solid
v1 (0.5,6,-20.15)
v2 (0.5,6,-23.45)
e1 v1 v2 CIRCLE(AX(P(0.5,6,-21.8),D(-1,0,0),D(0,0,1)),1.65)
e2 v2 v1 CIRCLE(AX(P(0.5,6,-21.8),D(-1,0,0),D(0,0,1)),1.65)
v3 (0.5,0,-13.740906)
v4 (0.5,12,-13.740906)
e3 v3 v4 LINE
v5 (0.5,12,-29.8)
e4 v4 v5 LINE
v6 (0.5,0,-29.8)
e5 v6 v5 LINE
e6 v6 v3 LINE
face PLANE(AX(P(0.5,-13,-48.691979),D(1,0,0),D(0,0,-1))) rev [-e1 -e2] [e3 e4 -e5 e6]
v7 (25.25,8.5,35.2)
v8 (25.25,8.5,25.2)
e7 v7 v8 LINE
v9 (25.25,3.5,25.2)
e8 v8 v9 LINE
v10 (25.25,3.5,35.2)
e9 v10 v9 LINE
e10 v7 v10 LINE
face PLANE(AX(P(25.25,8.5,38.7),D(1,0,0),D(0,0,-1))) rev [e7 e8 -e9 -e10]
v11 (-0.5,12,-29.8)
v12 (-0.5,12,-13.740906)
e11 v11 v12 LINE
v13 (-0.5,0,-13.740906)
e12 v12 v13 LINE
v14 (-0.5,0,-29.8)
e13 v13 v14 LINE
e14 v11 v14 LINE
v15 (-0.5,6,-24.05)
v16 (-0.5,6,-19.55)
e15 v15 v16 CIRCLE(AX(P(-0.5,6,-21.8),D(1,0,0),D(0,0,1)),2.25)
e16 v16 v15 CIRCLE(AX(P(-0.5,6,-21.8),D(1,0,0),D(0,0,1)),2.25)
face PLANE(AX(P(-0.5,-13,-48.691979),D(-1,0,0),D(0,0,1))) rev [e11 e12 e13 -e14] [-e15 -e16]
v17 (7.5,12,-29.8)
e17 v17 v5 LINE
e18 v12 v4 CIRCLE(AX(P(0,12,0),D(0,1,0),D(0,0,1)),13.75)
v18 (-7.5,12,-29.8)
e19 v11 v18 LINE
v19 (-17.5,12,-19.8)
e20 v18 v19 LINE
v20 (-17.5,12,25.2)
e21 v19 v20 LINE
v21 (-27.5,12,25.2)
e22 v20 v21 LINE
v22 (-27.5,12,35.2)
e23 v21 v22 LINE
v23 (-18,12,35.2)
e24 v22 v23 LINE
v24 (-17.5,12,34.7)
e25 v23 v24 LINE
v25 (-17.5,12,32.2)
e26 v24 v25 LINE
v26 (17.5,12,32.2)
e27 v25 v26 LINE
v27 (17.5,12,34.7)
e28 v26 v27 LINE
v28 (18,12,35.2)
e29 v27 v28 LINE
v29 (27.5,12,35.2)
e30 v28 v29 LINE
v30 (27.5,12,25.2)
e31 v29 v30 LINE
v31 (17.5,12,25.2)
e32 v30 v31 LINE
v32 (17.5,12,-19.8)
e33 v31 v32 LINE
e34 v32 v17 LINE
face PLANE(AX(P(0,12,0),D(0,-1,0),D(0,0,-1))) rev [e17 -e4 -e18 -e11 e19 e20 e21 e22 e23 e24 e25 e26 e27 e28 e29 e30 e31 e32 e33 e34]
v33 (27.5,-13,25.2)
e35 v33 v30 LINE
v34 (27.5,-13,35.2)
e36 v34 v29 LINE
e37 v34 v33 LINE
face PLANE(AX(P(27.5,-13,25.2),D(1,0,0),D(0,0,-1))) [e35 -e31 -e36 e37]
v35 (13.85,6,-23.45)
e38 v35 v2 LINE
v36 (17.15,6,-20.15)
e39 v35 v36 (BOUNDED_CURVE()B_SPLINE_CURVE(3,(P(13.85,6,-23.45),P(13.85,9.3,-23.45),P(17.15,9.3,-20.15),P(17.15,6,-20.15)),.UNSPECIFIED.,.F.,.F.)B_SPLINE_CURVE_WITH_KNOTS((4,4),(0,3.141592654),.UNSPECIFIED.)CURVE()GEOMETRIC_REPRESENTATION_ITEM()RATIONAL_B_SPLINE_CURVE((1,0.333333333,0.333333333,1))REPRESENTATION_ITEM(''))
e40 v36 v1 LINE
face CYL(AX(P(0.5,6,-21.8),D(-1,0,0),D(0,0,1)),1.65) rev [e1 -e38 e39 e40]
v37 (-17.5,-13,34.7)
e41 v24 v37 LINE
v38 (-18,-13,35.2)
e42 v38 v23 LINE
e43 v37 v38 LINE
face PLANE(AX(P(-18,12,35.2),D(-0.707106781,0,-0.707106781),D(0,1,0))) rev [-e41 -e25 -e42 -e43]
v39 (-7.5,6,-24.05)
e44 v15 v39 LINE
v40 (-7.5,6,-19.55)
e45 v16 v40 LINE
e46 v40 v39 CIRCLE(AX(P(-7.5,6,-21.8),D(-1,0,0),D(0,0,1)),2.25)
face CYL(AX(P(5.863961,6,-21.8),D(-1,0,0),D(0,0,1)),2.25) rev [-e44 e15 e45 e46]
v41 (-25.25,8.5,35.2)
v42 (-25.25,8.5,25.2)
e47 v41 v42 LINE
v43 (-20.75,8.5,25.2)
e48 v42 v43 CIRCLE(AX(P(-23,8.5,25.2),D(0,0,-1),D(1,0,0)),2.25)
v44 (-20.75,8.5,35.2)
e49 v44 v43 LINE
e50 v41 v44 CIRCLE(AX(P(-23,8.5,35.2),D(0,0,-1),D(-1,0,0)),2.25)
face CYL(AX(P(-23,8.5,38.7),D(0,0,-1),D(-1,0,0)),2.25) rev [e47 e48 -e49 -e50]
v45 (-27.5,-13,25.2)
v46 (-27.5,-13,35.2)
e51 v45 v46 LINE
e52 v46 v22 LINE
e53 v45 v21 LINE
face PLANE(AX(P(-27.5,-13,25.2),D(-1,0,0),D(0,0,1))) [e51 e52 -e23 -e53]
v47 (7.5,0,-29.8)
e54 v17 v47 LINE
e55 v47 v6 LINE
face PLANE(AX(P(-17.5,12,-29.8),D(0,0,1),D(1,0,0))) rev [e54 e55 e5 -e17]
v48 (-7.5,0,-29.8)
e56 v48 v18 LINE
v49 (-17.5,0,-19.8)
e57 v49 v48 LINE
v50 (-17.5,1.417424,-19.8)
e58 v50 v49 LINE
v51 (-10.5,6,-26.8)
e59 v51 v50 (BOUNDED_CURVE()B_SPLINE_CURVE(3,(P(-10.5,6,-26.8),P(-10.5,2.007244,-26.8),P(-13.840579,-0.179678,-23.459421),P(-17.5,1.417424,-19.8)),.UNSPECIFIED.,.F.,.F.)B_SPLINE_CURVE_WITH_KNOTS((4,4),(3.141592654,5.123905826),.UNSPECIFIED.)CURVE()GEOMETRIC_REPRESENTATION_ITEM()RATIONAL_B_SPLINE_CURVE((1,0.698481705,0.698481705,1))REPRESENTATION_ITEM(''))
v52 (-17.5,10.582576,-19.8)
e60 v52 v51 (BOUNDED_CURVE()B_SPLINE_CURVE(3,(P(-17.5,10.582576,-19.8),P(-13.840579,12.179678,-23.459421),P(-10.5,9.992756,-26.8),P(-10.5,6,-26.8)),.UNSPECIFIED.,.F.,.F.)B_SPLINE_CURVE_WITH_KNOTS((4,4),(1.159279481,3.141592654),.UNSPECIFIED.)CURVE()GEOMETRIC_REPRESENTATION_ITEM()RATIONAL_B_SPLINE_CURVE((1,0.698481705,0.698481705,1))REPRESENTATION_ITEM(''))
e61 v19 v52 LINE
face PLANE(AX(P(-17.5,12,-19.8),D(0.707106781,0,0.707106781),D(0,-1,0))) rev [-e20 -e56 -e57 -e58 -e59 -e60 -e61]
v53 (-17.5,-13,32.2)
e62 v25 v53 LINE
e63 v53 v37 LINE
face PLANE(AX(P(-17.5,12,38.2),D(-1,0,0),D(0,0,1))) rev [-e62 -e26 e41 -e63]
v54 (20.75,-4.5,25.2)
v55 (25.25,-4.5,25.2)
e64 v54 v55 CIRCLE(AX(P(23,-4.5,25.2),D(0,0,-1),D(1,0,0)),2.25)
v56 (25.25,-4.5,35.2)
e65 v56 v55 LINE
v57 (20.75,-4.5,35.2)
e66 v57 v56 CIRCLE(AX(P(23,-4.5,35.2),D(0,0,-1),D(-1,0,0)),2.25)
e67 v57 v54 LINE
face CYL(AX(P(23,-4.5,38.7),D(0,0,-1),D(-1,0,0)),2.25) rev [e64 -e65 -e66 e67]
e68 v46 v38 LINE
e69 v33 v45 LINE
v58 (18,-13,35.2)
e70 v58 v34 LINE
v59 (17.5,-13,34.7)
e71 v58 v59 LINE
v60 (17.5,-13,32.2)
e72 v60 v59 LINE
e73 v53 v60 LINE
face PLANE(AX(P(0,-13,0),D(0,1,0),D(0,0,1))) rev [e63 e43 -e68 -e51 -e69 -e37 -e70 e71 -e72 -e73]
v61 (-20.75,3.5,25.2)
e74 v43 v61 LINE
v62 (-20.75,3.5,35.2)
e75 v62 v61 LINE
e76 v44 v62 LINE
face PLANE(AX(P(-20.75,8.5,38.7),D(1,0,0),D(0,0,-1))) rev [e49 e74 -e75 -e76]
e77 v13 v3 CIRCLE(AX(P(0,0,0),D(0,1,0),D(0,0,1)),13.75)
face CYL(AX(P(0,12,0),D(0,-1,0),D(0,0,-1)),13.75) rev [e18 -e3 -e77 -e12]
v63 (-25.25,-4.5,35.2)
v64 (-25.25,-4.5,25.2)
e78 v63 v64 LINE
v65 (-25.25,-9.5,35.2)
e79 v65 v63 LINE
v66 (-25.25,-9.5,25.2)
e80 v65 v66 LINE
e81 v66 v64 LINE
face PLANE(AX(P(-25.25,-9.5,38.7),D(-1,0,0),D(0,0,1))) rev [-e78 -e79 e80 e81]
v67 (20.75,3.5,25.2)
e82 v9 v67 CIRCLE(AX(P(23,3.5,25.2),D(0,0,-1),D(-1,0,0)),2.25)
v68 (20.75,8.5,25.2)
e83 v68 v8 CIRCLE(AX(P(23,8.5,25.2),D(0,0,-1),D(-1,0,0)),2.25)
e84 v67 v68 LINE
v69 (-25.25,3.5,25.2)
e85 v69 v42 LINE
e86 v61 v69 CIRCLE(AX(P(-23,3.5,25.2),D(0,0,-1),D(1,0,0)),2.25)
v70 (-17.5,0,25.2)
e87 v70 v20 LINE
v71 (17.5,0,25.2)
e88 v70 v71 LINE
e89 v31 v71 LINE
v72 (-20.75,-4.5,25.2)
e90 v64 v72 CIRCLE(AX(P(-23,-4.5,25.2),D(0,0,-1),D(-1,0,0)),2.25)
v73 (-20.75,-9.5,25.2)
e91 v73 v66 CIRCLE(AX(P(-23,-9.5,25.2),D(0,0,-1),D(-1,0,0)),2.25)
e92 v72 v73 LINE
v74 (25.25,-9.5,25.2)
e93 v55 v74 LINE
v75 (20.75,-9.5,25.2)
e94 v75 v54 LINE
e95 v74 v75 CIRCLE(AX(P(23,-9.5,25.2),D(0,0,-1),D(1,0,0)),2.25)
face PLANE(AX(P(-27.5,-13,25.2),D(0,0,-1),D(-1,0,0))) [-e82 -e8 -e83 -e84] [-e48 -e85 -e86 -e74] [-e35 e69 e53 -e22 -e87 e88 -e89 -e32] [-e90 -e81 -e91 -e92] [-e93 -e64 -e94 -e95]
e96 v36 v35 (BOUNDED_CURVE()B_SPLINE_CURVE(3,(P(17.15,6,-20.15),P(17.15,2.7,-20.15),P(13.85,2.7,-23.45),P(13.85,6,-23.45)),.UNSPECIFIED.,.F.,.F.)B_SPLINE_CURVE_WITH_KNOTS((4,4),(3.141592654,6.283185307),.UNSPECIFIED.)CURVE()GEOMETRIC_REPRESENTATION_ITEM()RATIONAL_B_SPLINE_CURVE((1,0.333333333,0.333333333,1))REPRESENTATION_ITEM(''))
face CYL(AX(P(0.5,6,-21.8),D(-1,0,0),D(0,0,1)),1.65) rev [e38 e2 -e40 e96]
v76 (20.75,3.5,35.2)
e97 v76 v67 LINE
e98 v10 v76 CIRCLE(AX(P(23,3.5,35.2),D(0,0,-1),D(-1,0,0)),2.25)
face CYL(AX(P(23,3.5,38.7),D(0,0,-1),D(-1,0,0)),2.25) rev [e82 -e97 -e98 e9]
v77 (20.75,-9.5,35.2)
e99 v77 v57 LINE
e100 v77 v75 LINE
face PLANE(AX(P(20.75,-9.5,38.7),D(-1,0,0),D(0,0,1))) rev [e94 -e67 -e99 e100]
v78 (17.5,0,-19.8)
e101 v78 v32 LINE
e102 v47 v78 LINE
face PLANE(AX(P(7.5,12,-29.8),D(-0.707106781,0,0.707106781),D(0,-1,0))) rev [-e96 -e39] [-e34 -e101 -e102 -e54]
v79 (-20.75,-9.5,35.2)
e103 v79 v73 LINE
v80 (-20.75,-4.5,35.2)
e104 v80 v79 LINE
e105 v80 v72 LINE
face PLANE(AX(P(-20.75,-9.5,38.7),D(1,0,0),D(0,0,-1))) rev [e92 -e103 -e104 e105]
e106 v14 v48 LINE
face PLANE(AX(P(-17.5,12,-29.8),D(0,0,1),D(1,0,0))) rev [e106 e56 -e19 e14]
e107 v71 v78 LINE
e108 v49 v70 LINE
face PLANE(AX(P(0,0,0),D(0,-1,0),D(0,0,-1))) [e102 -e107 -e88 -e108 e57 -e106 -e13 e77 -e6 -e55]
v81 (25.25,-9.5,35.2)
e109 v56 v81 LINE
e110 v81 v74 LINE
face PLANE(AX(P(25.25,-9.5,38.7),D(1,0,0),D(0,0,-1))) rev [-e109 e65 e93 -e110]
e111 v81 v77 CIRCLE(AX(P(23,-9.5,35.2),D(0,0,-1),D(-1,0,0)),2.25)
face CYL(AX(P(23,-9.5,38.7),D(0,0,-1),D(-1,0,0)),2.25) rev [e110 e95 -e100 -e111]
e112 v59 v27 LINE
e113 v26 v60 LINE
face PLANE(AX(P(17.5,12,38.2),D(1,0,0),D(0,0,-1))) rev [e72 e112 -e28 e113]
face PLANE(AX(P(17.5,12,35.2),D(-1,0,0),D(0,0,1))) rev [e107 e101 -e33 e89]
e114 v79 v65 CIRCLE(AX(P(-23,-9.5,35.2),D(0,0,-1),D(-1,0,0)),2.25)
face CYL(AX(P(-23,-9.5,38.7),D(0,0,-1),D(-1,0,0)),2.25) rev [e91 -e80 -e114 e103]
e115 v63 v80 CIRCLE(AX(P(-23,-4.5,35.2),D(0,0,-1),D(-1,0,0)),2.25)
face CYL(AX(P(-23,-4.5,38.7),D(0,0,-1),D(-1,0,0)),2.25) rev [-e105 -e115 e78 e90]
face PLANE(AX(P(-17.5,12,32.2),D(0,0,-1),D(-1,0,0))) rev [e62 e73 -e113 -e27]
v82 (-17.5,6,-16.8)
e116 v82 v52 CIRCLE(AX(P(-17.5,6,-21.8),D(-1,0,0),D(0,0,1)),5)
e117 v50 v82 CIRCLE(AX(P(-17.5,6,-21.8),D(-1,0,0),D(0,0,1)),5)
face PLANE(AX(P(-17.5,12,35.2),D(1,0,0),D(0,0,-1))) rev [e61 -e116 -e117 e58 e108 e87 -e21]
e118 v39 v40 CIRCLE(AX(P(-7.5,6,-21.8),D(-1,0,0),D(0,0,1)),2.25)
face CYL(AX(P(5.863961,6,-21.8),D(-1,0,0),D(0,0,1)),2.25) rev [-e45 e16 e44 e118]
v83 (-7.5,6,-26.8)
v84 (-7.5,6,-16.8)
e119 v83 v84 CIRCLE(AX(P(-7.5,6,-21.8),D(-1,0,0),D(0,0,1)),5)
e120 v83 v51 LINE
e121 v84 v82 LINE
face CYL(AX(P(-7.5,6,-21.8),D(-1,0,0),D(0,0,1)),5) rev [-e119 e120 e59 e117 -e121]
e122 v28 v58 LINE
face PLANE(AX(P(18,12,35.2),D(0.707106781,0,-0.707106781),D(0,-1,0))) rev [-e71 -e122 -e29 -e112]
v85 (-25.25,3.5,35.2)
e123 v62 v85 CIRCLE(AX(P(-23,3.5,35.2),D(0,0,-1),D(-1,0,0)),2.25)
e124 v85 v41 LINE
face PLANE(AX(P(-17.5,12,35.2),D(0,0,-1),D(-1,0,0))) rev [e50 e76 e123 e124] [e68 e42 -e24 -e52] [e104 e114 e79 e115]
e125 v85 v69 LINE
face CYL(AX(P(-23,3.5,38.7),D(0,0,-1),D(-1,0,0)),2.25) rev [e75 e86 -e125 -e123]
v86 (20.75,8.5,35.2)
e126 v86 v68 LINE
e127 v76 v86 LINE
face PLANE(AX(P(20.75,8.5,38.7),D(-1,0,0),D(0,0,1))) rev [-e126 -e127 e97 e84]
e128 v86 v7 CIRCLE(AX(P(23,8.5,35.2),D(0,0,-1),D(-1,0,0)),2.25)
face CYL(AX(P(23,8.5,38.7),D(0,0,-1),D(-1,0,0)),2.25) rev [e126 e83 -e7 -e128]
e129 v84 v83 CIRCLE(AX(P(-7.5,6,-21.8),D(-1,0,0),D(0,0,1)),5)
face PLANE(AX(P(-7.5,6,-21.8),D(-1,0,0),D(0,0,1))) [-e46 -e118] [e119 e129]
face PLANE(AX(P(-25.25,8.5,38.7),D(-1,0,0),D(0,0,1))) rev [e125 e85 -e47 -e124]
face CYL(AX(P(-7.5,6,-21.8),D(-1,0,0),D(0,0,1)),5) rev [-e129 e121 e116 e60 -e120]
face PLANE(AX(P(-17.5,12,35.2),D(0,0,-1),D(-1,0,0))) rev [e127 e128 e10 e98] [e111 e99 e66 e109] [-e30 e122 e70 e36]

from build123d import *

# Parameters (mm, degrees)
SKETCH1_W           = 35
SKETCH1_H           = 65
SKETCH1_R           = 13.75
BOSS_EXTRUDE1_DEPTH = 12
CHAMFER1_SIZE       = 10
SKETCH2_W           = 55
SKETCH2_H           = 10
BOSS_EXTRUDE2_DEPTH = 25
SKETCH3_W           = 35
SKETCH3_H           = 6
CUT_EXTRUDE1_DEPTH  = 52.188768299
CUT_EXTRUDE2_DEPTH  = 13.5
CHAMFER2_SIZE       = 0.5
SKETCH5_W           = 1
SKETCH5_H           = 37.783958766
CUT_EXTRUDE3_DEPTH  = 52.188768299
SKETCH6_R           = 5
CUT_EXTRUDE4_DEPTH  = 10
SKETCH7_R           = 2.25
CUT_EXTRUDE5_DEPTH  = 7
M4_TAPPED_HOLE1_D   = 3.3


with BuildPart() as part:
    # Sketch1 → Boss-Extrude1 (new body)
    with BuildSketch(Plane(origin=(0, 0, 0), x_dir=(1, 0, 0), z_dir=(0, 1, 0))):
        with Locations((0, -2.7)):
            Rectangle(SKETCH1_W, SKETCH1_H)
        with Locations(Location((0, 0, 0), (0, 0, 270))):
            Circle(SKETCH1_R, mode=Mode.SUBTRACT)
    extrude(amount=BOSS_EXTRUDE1_DEPTH)

    # Chamfer1
    chamfer1_edges = [part.edges().sort_by_distance(p)[0] for p in [
        (-17.5, 6, -29.8),
        (17.5, 6, -29.8),
    ]]
    chamfer(chamfer1_edges, length=CHAMFER1_SIZE)

    # Sketch2 → Boss-Extrude2 (add)
    with BuildSketch(Plane(origin=(0, 12, 0), x_dir=(1, 0, 0), z_dir=(0, 1, 0))):
        with Locations((0, -30.2)):
            Rectangle(SKETCH2_W, SKETCH2_H)
    extrude(amount=-BOSS_EXTRUDE2_DEPTH)

    # Sketch3 → Cut-Extrude1 (cut, through all)
    with BuildSketch(Plane.XZ.offset(13)):
        with Locations((0, 35.2)):
            Rectangle(SKETCH3_W, SKETCH3_H)
    extrude(amount=-CUT_EXTRUDE1_DEPTH, mode=Mode.SUBTRACT)

    # Sketch4 → Cut-Extrude2 (cut)
    with BuildSketch(Plane(origin=(0, 0, 25.2), x_dir=(-1, 0, 0), z_dir=(0, 0, -1))):
        with BuildLine():
            Line((-20.75, 8.5), (-20.75, 3.5))
            ThreePointArc((-20.75, 3.5), (-23, 1.25), (-25.25, 3.5))
            Line((-25.25, 3.5), (-25.25, 8.5))
            ThreePointArc((-25.25, 8.5), (-23, 10.75), (-20.75, 8.5))
        make_face()
        with BuildLine():
            Line((20.75, 8.5), (20.75, 3.5))
            ThreePointArc((20.75, 3.5), (23, 1.25), (25.25, 3.5))
            Line((25.25, 3.5), (25.25, 8.5))
            ThreePointArc((25.25, 8.5), (23, 10.75), (20.75, 8.5))
        make_face()
        with BuildLine():
            Line((20.75, -9.5), (20.75, -4.5))
            ThreePointArc((20.75, -4.5), (23, -2.25), (25.25, -4.5))
            Line((25.25, -4.5), (25.25, -9.5))
            ThreePointArc((25.25, -9.5), (23, -11.75), (20.75, -9.5))
        make_face()
        with BuildLine():
            Line((-20.75, -9.5), (-20.75, -4.5))
            ThreePointArc((-20.75, -4.5), (-23, -2.25), (-25.25, -4.5))
            Line((-25.25, -4.5), (-25.25, -9.5))
            ThreePointArc((-25.25, -9.5), (-23, -11.75), (-20.75, -9.5))
        make_face()
    extrude(amount=-CUT_EXTRUDE2_DEPTH, mode=Mode.SUBTRACT)

    # Chamfer2
    chamfer2_edges = [part.edges().sort_by_distance(p)[0] for p in [
        (17.5, -0.5, 35.2),
        (-17.5, -0.5, 35.2),
    ]]
    chamfer(chamfer2_edges, length=CHAMFER2_SIZE)

    # Sketch5 → Cut-Extrude3 (cut, through all)
    with BuildSketch(Plane(origin=(0, 12, 0), x_dir=(1, 0, 0), z_dir=(0, 1, 0))):
        with Locations((0, 29.8)):
            Rectangle(SKETCH5_W, SKETCH5_H)
    extrude(amount=-CUT_EXTRUDE3_DEPTH, mode=Mode.SUBTRACT)

    # Sketch6 → Cut-Extrude4 (cut)
    with BuildSketch(Plane.ZY.offset(17.5)):
        with Locations((-21.8, 6)):
            Circle(SKETCH6_R)
    extrude(amount=-CUT_EXTRUDE4_DEPTH, mode=Mode.SUBTRACT)

    # Sketch7 → Cut-Extrude5 (cut)
    with BuildSketch(Plane.ZY.offset(7.5)):
        with Locations((-21.8, 6)):
            Circle(SKETCH7_R)
    extrude(amount=-CUT_EXTRUDE5_DEPTH, mode=Mode.SUBTRACT)

    # M4 Tapped Hole1 (through all)
    with Locations(Plane.ZY.offset(-0.5)):
        with Locations((-21.8, 6)):
            Hole(M4_TAPPED_HOLE1_D / 2)


solid = part.part
